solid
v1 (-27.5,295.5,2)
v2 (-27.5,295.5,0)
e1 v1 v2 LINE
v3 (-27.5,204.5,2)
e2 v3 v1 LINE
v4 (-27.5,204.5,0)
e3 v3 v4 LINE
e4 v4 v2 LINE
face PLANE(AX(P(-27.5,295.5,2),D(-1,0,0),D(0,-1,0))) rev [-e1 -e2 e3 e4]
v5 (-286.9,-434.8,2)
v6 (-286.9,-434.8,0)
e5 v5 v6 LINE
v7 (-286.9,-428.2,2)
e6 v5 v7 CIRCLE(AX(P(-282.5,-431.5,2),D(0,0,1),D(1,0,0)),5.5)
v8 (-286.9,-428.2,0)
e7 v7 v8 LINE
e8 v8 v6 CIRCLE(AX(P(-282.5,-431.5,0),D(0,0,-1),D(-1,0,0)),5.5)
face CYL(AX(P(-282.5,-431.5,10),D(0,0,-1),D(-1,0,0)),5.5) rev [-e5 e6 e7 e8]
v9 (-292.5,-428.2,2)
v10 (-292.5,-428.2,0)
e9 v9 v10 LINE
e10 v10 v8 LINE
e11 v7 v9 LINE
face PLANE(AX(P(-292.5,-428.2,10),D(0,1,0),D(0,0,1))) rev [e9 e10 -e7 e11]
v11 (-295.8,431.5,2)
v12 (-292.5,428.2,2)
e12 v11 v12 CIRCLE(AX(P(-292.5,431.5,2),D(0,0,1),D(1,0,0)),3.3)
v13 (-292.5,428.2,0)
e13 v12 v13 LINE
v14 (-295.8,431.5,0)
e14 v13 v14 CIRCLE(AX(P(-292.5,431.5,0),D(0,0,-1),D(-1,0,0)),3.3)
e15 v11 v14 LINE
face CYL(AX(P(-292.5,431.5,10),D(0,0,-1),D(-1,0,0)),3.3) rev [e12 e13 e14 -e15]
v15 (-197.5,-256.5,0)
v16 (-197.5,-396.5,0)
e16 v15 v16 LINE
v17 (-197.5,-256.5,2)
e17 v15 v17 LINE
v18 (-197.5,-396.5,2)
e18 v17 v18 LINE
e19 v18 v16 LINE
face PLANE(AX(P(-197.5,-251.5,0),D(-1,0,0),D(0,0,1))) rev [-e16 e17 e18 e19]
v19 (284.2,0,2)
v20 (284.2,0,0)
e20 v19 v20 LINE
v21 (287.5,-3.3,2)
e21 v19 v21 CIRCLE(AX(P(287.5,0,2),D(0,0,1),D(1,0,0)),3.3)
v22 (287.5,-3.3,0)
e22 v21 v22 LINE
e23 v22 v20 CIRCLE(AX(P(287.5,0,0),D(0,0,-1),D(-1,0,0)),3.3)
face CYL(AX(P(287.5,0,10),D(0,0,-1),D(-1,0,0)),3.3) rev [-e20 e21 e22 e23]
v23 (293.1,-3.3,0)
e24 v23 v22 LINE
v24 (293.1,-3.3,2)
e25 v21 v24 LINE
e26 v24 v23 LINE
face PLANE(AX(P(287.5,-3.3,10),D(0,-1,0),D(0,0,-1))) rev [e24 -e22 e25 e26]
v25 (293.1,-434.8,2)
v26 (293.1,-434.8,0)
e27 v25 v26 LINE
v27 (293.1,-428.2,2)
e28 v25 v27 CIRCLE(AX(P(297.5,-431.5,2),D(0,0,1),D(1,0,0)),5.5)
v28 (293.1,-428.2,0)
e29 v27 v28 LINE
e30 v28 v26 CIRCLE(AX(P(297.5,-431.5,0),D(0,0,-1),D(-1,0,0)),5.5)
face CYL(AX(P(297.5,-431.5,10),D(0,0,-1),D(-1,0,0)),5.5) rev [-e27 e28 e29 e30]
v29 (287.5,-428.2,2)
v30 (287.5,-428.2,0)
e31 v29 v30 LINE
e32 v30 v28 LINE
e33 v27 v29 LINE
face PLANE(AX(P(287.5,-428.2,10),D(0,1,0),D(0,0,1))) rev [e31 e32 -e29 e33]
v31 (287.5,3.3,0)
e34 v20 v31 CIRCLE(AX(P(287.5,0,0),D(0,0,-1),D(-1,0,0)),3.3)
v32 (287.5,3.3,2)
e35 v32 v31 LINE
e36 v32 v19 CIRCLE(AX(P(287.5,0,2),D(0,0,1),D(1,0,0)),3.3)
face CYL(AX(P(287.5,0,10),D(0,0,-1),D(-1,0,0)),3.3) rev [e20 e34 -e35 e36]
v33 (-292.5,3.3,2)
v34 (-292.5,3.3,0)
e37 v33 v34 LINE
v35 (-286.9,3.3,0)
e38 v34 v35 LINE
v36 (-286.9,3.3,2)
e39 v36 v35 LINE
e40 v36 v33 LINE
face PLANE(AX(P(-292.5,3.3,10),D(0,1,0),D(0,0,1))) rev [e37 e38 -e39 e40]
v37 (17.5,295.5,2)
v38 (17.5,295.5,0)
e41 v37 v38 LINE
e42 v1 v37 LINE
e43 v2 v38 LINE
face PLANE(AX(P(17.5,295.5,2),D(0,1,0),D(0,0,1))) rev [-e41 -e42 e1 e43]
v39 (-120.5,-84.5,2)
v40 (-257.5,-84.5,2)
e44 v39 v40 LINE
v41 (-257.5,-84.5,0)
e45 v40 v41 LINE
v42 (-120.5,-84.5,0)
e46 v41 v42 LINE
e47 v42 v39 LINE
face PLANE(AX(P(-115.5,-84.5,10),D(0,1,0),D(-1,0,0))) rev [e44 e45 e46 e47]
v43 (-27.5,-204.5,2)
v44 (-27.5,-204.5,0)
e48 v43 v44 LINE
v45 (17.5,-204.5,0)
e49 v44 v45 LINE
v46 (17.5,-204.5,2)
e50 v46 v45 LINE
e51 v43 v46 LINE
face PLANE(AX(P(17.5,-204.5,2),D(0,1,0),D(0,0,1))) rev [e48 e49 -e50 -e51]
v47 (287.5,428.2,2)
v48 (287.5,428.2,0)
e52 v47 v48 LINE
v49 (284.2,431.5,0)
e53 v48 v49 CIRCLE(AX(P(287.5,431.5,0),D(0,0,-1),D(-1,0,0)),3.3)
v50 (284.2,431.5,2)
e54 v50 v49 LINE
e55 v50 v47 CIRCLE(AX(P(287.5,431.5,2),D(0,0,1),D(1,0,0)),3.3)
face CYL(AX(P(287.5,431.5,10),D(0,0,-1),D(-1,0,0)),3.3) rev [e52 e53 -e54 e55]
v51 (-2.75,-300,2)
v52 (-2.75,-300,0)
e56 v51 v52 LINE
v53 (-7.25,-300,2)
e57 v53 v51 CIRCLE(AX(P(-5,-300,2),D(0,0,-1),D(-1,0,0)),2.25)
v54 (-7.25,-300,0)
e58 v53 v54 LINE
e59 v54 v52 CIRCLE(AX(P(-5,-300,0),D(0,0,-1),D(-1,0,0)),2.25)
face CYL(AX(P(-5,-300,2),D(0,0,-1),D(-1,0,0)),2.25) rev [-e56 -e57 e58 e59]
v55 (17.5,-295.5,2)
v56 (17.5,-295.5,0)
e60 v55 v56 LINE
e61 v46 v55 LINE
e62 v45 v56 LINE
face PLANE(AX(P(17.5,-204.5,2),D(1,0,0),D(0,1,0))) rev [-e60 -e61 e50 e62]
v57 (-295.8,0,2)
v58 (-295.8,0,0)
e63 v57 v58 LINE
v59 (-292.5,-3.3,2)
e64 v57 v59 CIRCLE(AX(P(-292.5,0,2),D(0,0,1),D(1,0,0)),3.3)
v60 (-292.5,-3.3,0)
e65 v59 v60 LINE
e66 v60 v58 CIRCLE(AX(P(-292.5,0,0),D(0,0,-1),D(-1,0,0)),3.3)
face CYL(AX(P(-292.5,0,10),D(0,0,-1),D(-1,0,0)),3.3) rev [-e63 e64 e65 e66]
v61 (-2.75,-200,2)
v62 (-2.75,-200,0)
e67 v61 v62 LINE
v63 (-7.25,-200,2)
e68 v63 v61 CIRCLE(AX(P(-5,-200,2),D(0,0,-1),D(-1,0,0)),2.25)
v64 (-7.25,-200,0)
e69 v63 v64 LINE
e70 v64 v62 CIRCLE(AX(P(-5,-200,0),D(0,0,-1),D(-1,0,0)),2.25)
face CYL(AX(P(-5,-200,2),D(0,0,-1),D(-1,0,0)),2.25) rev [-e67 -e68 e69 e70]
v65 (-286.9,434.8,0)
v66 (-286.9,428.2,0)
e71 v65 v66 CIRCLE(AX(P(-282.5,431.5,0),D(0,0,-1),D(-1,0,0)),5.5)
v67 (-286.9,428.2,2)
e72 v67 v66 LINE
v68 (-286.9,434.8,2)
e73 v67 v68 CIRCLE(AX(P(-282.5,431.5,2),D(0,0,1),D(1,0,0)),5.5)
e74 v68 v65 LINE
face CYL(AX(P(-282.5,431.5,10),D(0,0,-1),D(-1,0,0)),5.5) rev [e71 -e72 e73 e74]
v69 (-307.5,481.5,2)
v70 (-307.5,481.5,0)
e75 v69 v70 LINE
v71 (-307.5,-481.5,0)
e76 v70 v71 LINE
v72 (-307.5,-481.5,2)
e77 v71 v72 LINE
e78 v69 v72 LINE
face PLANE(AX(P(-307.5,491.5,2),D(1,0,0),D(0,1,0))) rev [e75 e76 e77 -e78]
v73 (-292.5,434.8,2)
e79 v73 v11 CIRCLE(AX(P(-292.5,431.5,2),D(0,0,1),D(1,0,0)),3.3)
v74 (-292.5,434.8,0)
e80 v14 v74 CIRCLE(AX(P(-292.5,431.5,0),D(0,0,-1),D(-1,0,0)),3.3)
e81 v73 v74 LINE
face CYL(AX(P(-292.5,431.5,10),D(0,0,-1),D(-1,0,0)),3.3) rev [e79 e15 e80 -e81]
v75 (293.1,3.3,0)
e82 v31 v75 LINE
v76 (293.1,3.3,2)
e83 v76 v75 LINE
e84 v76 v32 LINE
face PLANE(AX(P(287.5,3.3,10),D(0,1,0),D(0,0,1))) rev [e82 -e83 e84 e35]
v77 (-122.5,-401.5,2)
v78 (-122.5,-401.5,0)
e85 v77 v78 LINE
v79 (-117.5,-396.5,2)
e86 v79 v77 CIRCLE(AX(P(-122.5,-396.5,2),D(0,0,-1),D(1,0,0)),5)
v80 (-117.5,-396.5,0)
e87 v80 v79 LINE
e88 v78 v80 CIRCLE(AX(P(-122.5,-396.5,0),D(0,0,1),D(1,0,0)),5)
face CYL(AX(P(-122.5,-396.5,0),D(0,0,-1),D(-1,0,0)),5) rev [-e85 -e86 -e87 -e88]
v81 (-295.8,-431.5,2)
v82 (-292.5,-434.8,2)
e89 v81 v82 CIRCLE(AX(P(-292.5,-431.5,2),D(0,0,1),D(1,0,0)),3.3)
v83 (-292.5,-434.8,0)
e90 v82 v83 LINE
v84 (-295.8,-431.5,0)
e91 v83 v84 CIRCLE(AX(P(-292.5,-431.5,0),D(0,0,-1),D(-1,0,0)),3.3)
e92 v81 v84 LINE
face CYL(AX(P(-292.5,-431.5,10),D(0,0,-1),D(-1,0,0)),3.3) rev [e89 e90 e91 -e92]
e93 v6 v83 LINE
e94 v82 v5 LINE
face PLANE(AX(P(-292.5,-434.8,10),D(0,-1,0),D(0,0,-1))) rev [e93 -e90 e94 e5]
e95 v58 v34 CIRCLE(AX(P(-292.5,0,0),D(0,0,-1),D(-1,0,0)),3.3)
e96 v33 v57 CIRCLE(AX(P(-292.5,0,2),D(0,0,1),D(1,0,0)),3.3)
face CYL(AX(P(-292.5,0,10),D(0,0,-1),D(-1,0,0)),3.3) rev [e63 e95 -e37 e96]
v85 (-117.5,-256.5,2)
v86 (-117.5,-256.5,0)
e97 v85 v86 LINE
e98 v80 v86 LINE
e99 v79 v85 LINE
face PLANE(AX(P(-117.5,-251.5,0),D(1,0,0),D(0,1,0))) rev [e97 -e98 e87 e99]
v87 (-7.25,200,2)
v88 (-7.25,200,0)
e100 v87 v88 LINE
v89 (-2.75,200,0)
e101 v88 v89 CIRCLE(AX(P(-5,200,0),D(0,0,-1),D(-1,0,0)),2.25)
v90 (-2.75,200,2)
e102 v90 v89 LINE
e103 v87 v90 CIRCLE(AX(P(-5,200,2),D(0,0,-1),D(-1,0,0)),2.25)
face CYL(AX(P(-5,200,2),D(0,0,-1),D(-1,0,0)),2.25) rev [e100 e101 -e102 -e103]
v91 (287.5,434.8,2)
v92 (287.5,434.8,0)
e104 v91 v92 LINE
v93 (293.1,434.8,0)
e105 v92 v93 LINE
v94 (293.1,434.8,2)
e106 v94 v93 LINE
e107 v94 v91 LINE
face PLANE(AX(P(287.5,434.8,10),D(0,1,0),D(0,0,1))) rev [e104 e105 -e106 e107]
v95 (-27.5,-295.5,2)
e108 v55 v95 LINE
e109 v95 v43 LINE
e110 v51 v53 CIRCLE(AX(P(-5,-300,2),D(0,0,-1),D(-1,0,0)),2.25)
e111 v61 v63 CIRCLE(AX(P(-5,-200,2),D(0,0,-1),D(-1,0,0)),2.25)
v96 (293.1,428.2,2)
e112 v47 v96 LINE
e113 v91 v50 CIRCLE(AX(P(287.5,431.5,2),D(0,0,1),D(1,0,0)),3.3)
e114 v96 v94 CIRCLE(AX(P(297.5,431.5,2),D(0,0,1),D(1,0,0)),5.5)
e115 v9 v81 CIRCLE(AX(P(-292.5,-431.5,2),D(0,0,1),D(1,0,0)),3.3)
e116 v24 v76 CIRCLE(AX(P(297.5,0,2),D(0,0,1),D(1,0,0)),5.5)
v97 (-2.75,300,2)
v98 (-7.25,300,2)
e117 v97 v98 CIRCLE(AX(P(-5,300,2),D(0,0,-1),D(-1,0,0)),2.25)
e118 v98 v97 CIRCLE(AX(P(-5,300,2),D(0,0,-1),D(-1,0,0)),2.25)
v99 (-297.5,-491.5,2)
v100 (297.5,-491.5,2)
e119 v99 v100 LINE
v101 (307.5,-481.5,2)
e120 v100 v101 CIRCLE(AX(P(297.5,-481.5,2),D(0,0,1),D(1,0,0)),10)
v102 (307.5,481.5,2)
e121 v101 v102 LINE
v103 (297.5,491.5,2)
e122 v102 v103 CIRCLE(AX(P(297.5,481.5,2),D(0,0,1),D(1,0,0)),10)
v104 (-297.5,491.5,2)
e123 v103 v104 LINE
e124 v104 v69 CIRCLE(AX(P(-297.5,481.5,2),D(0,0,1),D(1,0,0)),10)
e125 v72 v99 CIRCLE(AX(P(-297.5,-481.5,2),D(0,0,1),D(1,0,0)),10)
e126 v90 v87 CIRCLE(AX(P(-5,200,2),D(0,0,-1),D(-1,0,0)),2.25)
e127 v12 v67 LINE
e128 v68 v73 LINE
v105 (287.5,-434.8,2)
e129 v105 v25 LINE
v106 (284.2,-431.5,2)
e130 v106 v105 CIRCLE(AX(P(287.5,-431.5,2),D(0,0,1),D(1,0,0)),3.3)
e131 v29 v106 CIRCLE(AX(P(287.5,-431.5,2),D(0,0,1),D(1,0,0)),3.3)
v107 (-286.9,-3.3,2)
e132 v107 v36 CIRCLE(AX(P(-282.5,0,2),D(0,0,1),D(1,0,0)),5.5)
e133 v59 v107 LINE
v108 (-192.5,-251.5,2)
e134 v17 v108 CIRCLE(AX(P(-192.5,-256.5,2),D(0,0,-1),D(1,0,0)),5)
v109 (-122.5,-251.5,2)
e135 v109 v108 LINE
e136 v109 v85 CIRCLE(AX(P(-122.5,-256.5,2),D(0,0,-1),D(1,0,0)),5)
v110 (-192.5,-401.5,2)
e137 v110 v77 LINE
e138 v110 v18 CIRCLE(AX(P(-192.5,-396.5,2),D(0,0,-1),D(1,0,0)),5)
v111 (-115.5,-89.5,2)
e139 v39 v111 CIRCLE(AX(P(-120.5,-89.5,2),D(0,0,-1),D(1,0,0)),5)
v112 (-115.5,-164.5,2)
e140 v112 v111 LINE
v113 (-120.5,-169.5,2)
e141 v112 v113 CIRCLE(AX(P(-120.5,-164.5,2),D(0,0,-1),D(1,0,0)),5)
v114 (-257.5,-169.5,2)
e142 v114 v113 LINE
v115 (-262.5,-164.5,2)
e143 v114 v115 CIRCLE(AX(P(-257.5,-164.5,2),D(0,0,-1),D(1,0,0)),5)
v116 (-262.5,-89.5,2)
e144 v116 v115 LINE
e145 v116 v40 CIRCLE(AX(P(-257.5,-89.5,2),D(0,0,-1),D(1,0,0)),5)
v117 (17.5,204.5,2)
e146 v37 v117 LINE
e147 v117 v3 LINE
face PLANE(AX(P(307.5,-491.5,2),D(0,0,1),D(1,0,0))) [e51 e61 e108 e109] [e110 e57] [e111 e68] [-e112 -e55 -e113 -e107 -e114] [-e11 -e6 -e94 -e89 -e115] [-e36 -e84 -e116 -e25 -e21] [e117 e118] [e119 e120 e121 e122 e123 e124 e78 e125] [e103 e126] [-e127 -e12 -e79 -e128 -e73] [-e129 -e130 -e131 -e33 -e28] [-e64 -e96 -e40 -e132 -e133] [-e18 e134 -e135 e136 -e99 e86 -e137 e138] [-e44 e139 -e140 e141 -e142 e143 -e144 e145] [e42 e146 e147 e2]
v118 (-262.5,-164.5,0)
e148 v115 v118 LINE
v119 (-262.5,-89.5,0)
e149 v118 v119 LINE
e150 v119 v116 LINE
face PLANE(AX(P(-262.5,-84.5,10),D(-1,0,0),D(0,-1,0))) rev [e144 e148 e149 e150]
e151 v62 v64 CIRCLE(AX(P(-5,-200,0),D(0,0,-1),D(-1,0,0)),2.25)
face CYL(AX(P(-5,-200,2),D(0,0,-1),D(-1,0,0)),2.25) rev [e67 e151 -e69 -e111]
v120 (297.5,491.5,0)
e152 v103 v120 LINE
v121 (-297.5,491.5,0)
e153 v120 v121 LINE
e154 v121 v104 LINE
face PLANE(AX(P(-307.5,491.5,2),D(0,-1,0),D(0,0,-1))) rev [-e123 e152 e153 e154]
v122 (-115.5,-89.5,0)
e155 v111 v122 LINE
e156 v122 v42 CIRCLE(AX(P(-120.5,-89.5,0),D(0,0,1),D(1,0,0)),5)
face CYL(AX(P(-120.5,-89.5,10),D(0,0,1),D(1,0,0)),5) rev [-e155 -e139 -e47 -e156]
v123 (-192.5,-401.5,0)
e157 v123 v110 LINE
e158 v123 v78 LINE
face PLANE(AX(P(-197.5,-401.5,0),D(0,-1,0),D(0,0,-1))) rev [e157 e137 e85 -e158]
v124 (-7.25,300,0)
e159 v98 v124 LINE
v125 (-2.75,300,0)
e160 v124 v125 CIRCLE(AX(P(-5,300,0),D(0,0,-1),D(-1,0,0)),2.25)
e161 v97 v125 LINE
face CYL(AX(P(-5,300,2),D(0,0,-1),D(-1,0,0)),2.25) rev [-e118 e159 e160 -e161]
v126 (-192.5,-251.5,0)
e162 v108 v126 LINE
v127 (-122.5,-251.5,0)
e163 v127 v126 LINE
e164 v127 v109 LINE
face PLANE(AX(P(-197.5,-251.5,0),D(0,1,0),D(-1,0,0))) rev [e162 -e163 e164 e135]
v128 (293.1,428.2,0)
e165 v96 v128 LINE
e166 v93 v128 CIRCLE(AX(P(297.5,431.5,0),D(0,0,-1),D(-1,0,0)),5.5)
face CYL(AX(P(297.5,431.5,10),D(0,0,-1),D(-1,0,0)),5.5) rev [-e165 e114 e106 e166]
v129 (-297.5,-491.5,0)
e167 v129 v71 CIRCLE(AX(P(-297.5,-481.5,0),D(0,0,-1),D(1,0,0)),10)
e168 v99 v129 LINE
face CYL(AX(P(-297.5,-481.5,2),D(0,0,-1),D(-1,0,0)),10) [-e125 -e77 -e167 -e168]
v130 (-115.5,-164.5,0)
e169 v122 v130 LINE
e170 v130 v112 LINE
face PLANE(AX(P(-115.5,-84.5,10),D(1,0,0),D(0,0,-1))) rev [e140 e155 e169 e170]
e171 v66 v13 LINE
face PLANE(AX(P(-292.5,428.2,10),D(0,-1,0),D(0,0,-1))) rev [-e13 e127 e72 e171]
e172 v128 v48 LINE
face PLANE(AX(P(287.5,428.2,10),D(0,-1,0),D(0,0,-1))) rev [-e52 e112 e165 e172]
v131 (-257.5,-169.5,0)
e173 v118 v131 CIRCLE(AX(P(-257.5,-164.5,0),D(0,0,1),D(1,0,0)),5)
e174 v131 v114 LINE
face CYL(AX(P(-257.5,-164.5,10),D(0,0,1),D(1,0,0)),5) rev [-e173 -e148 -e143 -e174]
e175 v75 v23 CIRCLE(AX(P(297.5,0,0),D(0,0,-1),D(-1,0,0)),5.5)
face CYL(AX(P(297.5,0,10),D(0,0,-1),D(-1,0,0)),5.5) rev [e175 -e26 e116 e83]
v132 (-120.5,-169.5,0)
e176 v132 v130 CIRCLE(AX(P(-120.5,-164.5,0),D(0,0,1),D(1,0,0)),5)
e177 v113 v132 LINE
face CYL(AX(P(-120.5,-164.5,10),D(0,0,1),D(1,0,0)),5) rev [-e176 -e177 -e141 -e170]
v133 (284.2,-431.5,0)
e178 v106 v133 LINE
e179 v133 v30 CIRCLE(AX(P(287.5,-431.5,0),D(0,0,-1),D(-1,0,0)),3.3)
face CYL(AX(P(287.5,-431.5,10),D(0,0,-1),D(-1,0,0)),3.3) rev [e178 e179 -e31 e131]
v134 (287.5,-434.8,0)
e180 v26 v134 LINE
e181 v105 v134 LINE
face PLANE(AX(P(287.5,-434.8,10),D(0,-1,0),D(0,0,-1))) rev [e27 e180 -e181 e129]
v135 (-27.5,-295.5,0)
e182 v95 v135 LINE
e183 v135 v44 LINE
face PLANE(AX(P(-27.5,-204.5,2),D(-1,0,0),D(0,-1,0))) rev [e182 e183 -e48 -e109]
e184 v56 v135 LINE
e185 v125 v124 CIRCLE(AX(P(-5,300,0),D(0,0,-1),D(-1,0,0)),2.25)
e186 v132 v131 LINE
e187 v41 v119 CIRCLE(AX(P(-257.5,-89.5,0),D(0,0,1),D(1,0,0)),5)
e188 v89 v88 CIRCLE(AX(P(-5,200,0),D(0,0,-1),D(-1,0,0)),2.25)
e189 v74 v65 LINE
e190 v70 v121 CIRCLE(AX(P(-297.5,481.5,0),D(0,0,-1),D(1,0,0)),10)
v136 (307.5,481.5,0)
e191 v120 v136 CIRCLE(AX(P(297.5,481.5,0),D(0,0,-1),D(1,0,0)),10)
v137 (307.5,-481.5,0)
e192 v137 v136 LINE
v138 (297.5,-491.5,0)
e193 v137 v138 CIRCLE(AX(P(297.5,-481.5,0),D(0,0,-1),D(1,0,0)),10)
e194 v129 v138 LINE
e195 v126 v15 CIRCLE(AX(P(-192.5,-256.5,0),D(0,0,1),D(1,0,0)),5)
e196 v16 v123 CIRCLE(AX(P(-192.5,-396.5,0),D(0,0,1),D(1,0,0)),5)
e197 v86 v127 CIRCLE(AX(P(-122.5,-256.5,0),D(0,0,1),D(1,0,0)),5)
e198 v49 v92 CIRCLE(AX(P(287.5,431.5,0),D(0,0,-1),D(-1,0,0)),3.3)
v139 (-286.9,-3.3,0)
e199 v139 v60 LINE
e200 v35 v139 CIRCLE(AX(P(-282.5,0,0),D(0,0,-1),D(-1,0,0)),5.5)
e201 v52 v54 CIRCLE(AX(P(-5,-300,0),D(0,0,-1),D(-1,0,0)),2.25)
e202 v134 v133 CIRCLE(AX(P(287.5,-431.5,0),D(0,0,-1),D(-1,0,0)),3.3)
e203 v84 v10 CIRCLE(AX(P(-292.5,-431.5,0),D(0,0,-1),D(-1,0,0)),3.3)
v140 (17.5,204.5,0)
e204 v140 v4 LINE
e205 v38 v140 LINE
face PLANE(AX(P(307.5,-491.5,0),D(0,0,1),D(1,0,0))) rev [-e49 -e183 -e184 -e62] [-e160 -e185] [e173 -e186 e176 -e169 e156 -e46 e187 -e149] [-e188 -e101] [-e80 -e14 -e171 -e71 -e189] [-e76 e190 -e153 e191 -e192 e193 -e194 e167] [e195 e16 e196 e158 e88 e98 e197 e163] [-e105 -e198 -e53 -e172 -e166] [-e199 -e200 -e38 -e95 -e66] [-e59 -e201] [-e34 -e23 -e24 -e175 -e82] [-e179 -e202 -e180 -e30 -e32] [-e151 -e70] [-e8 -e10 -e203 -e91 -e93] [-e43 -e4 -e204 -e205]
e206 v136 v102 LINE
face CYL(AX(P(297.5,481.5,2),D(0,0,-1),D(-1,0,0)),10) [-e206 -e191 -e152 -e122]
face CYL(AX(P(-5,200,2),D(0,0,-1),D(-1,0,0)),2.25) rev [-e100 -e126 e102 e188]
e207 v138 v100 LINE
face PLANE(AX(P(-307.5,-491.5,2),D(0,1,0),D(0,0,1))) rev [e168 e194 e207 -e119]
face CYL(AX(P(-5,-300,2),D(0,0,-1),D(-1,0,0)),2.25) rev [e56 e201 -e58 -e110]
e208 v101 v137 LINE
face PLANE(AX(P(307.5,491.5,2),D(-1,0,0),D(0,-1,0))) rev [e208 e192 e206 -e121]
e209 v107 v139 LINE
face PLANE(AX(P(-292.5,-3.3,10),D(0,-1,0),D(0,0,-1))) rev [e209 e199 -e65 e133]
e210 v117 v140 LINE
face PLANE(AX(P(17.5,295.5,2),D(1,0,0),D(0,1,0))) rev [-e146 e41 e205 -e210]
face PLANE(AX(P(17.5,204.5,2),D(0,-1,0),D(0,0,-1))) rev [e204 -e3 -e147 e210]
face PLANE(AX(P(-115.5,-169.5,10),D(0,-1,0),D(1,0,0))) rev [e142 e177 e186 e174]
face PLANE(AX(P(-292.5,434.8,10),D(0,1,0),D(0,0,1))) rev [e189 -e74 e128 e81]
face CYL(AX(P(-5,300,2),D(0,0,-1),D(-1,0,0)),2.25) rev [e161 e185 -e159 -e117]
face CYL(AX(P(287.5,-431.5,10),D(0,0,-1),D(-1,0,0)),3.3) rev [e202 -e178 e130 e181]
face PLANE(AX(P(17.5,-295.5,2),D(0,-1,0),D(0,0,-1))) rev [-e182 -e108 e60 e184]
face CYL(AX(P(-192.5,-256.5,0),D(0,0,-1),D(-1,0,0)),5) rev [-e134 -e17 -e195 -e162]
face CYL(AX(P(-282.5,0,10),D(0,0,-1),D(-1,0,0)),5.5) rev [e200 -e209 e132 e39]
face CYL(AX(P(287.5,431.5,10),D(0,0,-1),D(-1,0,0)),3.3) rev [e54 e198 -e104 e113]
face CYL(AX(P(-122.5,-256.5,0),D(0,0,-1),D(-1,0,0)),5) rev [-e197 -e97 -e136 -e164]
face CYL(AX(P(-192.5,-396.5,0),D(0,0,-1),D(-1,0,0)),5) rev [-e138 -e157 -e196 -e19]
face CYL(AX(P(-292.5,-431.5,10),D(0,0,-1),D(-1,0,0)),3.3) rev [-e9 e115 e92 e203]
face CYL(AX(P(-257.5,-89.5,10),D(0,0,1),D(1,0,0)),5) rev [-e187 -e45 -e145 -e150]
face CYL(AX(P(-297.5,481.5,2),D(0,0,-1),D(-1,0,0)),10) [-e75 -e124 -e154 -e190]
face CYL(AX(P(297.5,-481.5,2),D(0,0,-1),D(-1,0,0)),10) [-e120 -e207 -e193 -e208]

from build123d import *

# Parameters (mm, degrees)
SKETCH1_W            = 615
SKETCH1_H            = 983
BOSS_EXTRUDE1_DEPTH  = 2
SKETCH7_W            = 45
SKETCH7_H            = 91
CUT_EXTRUDE4_DEPTH   = 580.76935069
SKETCH8_R            = 2.25
CUT_EXTRUDE5_DEPTH   = 580.76935069
FILLET3_R            = 10
CUT_EXTRUDE6_DEPTH   = 10
LPATTERN1_COUNT      = 3
LPATTERN1_PITCH      = 431.5
LPATTERN1_COUNT_DIR2 = 2
LPATTERN1_PITCH_DIR2 = 580
SKETCH12_W           = 80
SKETCH12_H           = 150
CUT_EXTRUDE8_DEPTH   = 580.76935069
SKETCH13_W           = 147
SKETCH13_H           = 85
CUT_EXTRUDE9_DEPTH   = 10
FILLET4_R            = 5


with BuildPart() as part:
    # Sketch1 → Boss-Extrude1 (new body)
    with BuildSketch(Plane.XY):
        Rectangle(SKETCH1_W, SKETCH1_H)
    extrude(amount=BOSS_EXTRUDE1_DEPTH)

    # Sketch7 → Cut-Extrude4 (cut, through all)
    with BuildSketch(Plane(origin=(0, 0, 0), x_dir=(-1, 0, 0), z_dir=(0, 0, -1))):
        with Locations((5, 250)):
            Rectangle(SKETCH7_W, SKETCH7_H)
        with Locations((5, -250)):
            Rectangle(SKETCH7_W, SKETCH7_H)
    extrude(amount=-CUT_EXTRUDE4_DEPTH, mode=Mode.SUBTRACT)

    # Sketch8 → Cut-Extrude5 (cut, through all)
    with BuildSketch(Plane(origin=(0, 0, 0), x_dir=(-1, 0, 0), z_dir=(0, 0, -1))):
        with Locations((5, 300)):
            Circle(SKETCH8_R)
        with Locations((5, 200)):
            Circle(SKETCH8_R)
        with Locations((5, -200)):
            Circle(SKETCH8_R)
        with Locations((5, -300)):
            Circle(SKETCH8_R)
    extrude(amount=-CUT_EXTRUDE5_DEPTH, mode=Mode.SUBTRACT)

    # Fillet3
    fillet3_edges = [part.edges().sort_by_distance(p)[0] for p in [
        (307.5, -491.5, 1),
        (-307.5, -491.5, 1),
        (-307.5, 491.5, 1),
        (307.5, 491.5, 1),
    ]]
    fillet(fillet3_edges, radius=FILLET3_R)

    # Sketch10 → Cut-Extrude6 (cut)
    with BuildSketch(Plane(origin=(0, 0, 0), x_dir=(-1, 0, 0), z_dir=(0, 0, -1))):
        with BuildLine():
            Line((292.5, 434.8), (286.9, 434.8))
            ThreePointArc((286.9, 434.8), (277, 431.5), (286.9, 428.2))
            Line((286.9, 428.2), (292.5, 428.2))
            ThreePointArc((292.5, 428.2), (295.8, 431.5), (292.5, 434.8))
        make_face()
    cut_extrude6 = extrude(amount=-CUT_EXTRUDE6_DEPTH, mode=Mode.SUBTRACT)

    # LPattern1: Cut-Extrude6 3 × 2
    with Locations(*[(j * LPATTERN1_PITCH_DIR2, -i * LPATTERN1_PITCH, 0) for i in range(LPATTERN1_COUNT) for j in range(LPATTERN1_COUNT_DIR2) if (i, j) != (0, 0)]):
        add(cut_extrude6, mode=Mode.SUBTRACT)

    # Sketch12 → Cut-Extrude8 (cut, through all)
    with BuildSketch(Plane.XY.offset(2)):
        with Locations((-157.5, -326.5)):
            Rectangle(SKETCH12_W, SKETCH12_H)
    extrude(amount=-CUT_EXTRUDE8_DEPTH, mode=Mode.SUBTRACT)

    # Sketch13 → Cut-Extrude9 (cut)
    with BuildSketch(Plane(origin=(0, 0, 0), x_dir=(-1, 0, 0), z_dir=(0, 0, -1))):
        with Locations((189, -127)):
            Rectangle(SKETCH13_W, SKETCH13_H)
    extrude(amount=-CUT_EXTRUDE9_DEPTH, mode=Mode.SUBTRACT)

    # Fillet4
    fillet4_edges = [part.edges().sort_by_distance(p)[0] for p in [
        (-197.5, -401.5, 1),
        (-197.5, -251.5, 1),
        (-117.5, -251.5, 1),
        (-117.5, -401.5, 1),
        (-115.5, -169.5, 1),
        (-115.5, -84.5, 1),
        (-262.5, -84.5, 1),
        (-262.5, -169.5, 1),
    ]]
    fillet(fillet4_edges, radius=FILLET4_R)


solid = part.part
